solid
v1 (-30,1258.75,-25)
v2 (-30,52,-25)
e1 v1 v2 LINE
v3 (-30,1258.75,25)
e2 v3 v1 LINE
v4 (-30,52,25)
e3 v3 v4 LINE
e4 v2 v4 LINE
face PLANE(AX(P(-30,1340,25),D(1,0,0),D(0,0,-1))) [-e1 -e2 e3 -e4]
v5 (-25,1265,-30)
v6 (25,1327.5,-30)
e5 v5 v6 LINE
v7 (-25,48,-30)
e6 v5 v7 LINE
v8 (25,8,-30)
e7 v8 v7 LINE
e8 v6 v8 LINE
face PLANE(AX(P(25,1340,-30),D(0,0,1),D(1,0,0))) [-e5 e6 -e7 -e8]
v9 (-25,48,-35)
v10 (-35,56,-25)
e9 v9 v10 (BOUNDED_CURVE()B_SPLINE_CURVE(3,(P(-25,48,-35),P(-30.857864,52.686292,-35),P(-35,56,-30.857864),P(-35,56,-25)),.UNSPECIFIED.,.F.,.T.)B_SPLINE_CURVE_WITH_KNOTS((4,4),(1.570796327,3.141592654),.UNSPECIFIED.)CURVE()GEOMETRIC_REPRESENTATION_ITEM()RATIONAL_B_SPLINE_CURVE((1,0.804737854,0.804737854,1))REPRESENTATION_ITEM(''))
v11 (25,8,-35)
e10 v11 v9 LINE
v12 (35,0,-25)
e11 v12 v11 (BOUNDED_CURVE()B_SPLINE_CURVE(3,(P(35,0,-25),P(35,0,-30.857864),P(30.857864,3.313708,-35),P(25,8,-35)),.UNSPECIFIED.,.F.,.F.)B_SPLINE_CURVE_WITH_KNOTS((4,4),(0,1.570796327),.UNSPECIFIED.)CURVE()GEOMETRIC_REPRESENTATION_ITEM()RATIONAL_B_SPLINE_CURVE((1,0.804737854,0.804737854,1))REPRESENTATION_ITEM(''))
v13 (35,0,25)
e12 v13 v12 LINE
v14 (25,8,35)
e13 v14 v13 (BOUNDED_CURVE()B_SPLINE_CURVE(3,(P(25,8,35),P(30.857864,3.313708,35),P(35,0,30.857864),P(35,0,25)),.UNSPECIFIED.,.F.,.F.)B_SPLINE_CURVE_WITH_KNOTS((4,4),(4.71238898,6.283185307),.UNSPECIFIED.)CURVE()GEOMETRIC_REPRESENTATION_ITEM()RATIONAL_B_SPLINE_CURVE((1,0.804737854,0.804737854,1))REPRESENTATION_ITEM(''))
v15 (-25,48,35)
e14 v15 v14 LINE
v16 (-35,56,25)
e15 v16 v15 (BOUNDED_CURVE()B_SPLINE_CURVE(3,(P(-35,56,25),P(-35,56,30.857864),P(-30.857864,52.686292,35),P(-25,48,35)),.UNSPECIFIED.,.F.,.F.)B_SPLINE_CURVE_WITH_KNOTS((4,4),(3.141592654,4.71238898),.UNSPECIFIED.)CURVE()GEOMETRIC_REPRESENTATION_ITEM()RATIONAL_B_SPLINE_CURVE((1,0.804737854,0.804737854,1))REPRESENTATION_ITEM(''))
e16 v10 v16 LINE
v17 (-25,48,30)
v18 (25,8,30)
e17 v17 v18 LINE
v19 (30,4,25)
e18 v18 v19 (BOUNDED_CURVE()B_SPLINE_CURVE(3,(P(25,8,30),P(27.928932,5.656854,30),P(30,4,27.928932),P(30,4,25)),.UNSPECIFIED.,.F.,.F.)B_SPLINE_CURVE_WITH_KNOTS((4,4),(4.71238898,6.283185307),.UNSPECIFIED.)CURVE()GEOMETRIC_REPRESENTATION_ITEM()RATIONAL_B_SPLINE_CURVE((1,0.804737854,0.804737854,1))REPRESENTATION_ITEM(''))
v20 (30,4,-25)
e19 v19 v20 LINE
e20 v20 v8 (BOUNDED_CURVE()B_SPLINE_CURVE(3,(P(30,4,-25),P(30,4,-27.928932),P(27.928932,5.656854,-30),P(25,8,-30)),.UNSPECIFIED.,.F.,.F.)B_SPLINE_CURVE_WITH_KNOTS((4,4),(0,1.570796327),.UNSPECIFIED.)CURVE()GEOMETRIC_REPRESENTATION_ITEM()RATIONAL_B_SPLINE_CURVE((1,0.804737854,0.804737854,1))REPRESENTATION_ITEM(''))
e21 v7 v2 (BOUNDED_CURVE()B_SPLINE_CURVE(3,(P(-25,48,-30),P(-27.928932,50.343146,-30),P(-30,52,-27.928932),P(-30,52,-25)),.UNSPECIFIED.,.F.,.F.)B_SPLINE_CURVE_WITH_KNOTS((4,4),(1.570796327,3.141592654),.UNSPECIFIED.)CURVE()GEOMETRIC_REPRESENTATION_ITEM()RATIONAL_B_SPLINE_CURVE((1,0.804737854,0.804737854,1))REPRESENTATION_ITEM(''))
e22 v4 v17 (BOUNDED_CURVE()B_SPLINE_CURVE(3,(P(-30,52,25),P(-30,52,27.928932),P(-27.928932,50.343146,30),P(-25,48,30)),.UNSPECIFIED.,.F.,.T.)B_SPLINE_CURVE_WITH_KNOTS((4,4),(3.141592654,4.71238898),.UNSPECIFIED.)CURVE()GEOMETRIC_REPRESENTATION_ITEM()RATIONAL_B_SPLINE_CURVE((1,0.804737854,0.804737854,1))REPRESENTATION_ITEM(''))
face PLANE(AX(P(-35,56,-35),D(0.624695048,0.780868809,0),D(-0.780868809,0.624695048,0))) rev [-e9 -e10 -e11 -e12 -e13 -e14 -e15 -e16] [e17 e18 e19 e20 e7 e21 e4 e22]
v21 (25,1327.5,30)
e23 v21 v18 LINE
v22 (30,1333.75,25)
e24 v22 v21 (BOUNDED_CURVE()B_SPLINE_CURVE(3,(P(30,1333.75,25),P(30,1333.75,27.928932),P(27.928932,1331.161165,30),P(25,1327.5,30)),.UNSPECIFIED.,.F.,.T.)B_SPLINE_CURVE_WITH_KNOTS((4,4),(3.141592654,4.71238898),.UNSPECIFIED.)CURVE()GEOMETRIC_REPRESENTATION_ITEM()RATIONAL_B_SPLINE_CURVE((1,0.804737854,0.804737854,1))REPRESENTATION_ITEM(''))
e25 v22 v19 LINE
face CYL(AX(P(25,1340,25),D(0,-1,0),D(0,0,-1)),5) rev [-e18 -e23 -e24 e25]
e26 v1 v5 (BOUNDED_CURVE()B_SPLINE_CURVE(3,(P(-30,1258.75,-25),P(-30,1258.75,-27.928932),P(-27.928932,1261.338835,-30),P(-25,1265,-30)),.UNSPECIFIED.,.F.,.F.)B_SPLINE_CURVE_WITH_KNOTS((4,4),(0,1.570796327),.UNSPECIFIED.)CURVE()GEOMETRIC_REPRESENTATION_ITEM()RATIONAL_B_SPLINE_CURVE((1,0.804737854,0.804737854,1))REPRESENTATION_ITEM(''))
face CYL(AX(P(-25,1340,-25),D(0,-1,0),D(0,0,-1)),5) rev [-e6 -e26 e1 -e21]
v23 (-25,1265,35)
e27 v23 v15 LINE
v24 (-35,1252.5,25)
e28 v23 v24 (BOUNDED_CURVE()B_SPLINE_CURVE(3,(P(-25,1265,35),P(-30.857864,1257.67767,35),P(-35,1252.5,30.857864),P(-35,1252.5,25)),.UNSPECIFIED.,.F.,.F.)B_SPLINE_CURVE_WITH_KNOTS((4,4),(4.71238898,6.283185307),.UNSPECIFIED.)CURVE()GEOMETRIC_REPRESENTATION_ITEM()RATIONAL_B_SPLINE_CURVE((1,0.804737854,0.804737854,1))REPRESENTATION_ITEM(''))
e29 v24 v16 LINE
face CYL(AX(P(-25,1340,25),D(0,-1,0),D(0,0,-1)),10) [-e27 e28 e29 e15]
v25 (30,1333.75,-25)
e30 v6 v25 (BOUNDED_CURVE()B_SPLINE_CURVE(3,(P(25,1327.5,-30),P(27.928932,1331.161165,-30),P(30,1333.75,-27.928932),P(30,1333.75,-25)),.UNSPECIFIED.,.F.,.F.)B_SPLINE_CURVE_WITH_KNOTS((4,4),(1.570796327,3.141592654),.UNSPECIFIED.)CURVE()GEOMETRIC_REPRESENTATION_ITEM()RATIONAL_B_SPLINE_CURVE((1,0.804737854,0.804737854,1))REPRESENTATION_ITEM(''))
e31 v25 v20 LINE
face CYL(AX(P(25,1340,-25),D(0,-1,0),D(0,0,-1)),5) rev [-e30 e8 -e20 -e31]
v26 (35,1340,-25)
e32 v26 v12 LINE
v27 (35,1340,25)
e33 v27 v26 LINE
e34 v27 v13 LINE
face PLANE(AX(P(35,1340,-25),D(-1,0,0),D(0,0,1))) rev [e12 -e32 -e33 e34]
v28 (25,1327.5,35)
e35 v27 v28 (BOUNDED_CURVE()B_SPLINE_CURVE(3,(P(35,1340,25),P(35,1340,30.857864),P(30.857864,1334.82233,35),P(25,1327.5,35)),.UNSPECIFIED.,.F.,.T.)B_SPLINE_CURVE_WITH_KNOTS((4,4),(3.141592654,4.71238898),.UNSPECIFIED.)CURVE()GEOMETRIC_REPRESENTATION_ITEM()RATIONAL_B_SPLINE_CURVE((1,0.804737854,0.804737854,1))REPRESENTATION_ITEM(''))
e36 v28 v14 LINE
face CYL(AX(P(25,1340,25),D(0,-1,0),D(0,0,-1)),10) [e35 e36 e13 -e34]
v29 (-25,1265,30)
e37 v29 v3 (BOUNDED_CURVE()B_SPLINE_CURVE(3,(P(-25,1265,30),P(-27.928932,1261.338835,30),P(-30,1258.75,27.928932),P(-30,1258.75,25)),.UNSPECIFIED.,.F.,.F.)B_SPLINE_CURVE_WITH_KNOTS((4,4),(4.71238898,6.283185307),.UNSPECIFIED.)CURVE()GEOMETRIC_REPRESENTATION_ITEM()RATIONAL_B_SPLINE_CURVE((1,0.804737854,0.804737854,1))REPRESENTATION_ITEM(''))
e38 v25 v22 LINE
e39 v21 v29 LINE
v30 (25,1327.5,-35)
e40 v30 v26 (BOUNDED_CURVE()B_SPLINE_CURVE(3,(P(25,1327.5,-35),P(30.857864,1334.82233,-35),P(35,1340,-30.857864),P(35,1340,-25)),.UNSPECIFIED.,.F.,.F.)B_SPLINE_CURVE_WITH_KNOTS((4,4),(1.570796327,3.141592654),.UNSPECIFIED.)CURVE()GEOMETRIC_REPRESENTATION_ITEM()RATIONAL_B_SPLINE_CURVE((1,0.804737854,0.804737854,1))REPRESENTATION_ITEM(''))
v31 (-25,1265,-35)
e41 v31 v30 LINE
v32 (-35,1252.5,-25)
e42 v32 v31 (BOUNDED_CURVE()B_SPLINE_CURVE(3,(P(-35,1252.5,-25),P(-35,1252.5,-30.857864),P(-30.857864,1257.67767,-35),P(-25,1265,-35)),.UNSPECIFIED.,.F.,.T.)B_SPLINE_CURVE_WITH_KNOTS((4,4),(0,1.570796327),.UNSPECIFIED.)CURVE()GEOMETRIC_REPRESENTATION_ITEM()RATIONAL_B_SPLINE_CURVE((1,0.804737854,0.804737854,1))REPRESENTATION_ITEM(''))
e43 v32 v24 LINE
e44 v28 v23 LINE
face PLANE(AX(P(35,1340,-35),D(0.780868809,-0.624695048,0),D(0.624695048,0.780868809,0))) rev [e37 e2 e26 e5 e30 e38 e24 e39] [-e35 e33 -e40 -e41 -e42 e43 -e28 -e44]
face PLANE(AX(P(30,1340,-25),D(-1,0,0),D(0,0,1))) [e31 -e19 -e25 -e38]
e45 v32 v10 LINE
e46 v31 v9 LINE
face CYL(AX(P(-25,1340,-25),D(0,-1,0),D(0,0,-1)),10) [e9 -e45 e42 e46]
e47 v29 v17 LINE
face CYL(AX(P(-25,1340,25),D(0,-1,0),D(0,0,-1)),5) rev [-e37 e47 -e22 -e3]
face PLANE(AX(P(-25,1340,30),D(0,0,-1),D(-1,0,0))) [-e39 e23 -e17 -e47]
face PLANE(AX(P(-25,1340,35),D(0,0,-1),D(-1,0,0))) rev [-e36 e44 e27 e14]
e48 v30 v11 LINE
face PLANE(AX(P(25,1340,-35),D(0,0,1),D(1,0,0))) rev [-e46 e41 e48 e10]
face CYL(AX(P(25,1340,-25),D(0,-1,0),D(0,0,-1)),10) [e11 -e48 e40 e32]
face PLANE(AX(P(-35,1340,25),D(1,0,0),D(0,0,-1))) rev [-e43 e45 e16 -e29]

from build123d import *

# Parameters (mm, degrees)
FEATURE_19_WELDMEMBERFEAT_4_MORE_IN_5_DEPTH = 1340
CUT_EXTRUDE1_DEPTH                          = 1343.283502096
CUT_EXTRUDE1_DEPTH_BACK                     = 1343.283502096


with BuildPart() as part:
    # Sketch1 → feature 19 (WeldMemberFeat) (+4 more in 5 files) Cold-formed Hollow Structural Square Steel(gb t6728-2002) 70×70×5(1) (new body)
    with BuildSketch(Plane(origin=(0, 0, 0), x_dir=(-1, 0, 0), z_dir=(0, 1, 0))):
        with BuildLine():
            Line((-25, -35), (25, -35))
            ThreePointArc((25, -35), (32.071067812, -32.071067812), (35, -25))
            Line((35, -25), (35, 25))
            ThreePointArc((35, 25), (32.071067812, 32.071067812), (25, 35))
            Line((25, 35), (-25, 35))
            ThreePointArc((-25, 35), (-32.071067812, 32.071067812), (-35, 25))
            Line((-35, 25), (-35, -25))
            ThreePointArc((-35, -25), (-32.071067812, -32.071067812), (-25, -35))
        make_face()
        with BuildLine():
            Line((-25, -30), (25, -30))
            ThreePointArc((25, -30), (28.535533906, -28.535533906), (30, -25))
            Line((30, -25), (30, 25))
            ThreePointArc((30, 25), (28.535533906, 28.535533906), (25, 30))
            Line((25, 30), (-25, 30))
            ThreePointArc((-25, 30), (-28.535533906, 28.535533906), (-30, 25))
            Line((-30, 25), (-30, -25))
            ThreePointArc((-30, -25), (-28.535533906, -28.535533906), (-25, -30))
        make_face(mode=Mode.SUBTRACT)
    extrude(amount=FEATURE_19_WELDMEMBERFEAT_4_MORE_IN_5_DEPTH)

    # 0:feat:20/0 feature 20/0 (ProfileFeature) (+11 more in 7 files) Sketch2 → Cut-Extrude1 (cut, two sides: drawn at the far end of the back side and taken through both)
    with BuildSketch(Plane.XY.offset(35).offset(-CUT_EXTRUDE1_DEPTH_BACK)):
        Polygon((35, 1340), (-35, 1252.5), (-35, 1340), align=None)
        Polygon((-35, 56), (35, 0), (-35, 0), align=None)
    extrude(amount=CUT_EXTRUDE1_DEPTH + CUT_EXTRUDE1_DEPTH_BACK, mode=Mode.SUBTRACT)


solid = part.part
